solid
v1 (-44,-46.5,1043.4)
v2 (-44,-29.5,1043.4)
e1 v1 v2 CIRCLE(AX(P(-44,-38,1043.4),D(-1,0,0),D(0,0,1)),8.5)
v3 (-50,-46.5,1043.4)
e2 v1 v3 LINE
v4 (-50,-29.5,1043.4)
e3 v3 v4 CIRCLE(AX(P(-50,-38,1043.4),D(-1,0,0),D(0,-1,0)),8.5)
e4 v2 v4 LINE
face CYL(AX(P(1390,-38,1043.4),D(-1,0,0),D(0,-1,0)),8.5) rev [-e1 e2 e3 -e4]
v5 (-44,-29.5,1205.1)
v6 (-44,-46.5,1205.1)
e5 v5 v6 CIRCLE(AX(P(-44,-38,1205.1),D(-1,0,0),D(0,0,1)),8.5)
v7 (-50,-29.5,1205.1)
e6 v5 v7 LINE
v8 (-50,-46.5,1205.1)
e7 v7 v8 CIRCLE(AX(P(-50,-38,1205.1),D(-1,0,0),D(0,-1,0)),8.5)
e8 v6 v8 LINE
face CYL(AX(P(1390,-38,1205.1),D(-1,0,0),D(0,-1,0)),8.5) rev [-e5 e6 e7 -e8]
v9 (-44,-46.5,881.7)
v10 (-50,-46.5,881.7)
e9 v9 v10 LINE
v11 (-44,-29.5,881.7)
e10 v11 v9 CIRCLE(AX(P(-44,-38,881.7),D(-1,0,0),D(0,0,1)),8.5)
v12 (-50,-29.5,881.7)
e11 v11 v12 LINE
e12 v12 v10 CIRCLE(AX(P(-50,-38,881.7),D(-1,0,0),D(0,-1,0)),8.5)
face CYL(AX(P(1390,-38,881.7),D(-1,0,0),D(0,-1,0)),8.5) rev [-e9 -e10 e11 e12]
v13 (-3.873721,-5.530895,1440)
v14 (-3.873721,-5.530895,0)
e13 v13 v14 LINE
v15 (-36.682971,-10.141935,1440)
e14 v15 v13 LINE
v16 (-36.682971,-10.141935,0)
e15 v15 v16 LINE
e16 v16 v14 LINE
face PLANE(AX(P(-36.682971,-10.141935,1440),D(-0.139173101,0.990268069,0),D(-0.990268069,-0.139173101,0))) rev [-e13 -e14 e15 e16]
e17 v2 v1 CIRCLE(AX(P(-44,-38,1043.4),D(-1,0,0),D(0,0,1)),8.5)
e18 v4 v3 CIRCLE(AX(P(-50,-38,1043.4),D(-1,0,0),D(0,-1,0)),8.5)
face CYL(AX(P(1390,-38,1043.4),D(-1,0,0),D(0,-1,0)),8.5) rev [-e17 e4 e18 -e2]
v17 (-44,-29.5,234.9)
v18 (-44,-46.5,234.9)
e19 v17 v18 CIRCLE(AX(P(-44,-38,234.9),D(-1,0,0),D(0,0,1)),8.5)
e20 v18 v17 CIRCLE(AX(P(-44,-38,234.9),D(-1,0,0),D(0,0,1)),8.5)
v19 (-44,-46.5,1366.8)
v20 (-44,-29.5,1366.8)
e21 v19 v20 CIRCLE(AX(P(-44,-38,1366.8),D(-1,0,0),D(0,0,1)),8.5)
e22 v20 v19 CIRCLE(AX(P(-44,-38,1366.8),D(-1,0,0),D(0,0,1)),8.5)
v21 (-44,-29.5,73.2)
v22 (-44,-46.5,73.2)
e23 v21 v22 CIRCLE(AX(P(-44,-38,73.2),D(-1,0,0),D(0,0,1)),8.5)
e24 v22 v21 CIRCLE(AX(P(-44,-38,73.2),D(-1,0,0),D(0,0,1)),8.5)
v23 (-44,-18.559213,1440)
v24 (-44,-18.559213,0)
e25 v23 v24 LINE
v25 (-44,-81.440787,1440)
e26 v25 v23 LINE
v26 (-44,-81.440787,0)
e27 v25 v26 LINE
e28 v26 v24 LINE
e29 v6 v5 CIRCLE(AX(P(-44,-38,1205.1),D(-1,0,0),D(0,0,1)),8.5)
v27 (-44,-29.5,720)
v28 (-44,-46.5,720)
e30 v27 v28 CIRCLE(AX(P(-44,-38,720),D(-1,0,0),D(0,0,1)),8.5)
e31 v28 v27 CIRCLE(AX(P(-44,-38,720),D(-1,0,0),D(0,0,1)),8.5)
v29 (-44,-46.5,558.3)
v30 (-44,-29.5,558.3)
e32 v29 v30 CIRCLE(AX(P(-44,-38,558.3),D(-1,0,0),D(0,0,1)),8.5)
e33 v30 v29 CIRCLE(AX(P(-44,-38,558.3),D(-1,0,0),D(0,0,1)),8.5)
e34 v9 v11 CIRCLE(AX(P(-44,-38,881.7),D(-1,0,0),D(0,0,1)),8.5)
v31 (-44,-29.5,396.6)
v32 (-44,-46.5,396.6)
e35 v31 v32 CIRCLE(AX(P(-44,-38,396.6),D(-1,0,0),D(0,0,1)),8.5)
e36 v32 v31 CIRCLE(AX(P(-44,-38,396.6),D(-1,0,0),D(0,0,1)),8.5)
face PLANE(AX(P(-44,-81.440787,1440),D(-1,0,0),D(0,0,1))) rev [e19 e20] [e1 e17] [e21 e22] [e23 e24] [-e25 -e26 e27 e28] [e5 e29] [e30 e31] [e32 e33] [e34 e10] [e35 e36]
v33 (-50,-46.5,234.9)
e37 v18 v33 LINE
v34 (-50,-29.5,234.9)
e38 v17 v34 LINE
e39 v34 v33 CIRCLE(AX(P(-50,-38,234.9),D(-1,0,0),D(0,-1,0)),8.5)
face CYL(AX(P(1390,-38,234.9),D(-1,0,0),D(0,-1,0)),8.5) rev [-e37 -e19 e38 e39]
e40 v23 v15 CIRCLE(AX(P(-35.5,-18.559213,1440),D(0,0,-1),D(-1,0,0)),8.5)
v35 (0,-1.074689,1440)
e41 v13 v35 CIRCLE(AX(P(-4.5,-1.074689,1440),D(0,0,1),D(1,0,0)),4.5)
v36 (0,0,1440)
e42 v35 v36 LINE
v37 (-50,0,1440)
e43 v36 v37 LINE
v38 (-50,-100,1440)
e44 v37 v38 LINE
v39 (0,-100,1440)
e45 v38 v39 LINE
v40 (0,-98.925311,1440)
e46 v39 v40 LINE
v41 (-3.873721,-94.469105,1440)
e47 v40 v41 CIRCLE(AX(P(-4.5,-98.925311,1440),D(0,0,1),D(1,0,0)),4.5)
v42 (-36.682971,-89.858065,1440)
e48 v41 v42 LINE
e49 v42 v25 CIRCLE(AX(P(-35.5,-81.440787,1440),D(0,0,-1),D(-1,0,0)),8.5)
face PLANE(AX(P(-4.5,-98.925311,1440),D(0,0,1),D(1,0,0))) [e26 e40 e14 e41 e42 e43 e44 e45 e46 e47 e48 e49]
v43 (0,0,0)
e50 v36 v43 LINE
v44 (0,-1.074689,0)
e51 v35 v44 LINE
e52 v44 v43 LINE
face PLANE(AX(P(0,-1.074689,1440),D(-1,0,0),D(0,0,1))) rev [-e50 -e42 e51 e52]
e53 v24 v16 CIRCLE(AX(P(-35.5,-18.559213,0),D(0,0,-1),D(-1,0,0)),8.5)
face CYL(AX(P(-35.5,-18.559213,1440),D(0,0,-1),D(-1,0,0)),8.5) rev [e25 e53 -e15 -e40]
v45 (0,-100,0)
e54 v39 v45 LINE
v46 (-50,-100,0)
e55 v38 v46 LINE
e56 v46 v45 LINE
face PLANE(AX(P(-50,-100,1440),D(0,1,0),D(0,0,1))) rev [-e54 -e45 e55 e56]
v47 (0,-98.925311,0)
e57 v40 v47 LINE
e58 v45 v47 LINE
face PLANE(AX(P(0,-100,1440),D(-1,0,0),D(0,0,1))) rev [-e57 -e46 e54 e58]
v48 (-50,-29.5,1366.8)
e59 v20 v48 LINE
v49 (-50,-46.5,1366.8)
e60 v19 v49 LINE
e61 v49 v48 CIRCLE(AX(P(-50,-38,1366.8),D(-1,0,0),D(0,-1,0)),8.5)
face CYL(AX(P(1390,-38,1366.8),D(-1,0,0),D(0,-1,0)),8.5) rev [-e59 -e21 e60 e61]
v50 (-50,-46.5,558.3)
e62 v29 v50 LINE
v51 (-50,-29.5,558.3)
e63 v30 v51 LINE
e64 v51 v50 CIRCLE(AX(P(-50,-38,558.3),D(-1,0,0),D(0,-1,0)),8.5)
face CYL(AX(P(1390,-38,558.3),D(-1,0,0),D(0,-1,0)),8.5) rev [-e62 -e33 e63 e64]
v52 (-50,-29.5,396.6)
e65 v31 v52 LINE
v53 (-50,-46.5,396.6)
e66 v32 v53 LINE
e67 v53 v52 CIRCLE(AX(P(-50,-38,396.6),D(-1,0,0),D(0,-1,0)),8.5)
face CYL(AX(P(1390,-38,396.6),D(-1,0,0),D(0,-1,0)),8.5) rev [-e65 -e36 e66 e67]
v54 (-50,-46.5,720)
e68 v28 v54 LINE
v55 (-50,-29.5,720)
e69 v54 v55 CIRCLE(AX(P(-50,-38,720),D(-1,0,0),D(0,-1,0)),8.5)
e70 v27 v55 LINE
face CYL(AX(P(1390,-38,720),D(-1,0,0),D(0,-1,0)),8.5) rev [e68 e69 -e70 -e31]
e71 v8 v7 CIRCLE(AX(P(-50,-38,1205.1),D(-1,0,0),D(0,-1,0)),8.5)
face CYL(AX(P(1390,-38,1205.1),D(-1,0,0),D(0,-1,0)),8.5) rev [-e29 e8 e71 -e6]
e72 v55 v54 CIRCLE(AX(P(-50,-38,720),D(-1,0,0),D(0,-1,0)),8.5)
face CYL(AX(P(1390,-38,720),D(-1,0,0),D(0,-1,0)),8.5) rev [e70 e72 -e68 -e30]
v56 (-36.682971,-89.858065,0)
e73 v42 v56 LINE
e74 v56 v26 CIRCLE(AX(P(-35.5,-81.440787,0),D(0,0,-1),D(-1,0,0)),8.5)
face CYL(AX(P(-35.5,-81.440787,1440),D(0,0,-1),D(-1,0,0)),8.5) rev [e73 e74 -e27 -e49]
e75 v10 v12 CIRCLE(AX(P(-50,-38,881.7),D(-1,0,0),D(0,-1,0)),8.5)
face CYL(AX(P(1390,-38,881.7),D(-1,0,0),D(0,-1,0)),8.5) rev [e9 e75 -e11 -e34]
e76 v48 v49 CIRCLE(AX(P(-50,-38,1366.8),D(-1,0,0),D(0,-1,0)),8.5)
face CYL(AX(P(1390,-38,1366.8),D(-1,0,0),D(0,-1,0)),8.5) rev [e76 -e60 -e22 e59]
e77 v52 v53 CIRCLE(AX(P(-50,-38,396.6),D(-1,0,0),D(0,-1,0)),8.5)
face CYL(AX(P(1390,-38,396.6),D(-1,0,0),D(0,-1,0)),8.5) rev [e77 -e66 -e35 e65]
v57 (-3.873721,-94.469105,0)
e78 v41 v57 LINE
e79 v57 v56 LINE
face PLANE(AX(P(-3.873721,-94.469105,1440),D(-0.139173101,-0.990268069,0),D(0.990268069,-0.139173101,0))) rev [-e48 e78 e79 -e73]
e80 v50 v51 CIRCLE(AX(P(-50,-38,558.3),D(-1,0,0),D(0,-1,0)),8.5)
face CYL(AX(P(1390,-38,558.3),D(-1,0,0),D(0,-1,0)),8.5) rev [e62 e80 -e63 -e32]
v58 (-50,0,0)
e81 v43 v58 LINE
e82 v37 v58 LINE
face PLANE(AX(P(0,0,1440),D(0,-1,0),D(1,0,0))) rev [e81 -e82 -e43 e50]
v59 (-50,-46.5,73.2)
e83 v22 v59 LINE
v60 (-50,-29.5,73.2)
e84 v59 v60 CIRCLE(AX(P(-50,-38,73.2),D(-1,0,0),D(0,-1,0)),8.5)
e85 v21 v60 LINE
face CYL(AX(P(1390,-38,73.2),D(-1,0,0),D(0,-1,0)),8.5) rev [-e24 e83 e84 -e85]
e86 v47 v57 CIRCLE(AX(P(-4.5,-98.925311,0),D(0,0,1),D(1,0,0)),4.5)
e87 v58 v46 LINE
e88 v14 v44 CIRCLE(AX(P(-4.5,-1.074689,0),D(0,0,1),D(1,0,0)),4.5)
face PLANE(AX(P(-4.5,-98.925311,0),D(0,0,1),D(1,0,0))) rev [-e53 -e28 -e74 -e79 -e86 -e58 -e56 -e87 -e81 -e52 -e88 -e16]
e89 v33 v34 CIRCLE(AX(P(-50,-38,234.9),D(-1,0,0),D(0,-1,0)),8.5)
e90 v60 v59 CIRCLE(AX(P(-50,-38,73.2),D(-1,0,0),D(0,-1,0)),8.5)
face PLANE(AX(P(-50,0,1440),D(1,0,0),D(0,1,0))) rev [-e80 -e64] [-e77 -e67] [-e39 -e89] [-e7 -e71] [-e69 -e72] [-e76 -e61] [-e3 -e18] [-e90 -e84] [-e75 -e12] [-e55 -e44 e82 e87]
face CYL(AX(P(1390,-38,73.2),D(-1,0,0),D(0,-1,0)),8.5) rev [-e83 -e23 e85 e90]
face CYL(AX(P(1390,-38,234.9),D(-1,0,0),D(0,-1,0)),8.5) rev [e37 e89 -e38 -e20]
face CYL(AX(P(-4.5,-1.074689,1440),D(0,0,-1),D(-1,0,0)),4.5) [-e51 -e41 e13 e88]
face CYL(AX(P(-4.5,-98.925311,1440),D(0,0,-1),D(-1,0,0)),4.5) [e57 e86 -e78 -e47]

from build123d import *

# Parameters (mm, degrees)
BOSS_EXTRUDE1_DEPTH = 1440
SKETCH2_R           = 8.5
CUT_EXTRUDE1_DEPTH  = 1440


with BuildPart() as part:
    # Sketch1 → Boss-Extrude1 (new body)
    with BuildSketch(Plane.XY):
        with BuildLine():
            Line((0, 0), (-50, 0))
            Line((-50, 0), (-50, -100))
            Line((-50, -100), (0, -100))
            Line((0, -100), (0, -98.925311188))
            ThreePointArc((0, -98.925311188), (-1.103806889, -95.973045557), (-3.873721046, -94.469104878))
            Line((-3.873721046, -94.469104878), (-36.682971358, -89.858065454))
            ThreePointArc((-36.682971358, -89.858065454), (-41.915031432, -87.017288616), (-44, -81.440786869))
            Line((-44, -81.440786869), (-44, -18.559213131))
            ThreePointArc((-44, -18.559213131), (-41.915031432, -12.982711384), (-36.682971358, -10.141934546))
            Line((-36.682971358, -10.141934546), (-3.873721046, -5.530895122))
            ThreePointArc((-3.873721046, -5.530895122), (-1.103806889, -4.026954443), (0, -1.074688812))
            Line((0, -1.074688812), (0, 0))
        make_face()
    extrude(amount=BOSS_EXTRUDE1_DEPTH)

    # Sketch2 → Cut-Extrude1 (cut)
    with BuildSketch(Plane.ZY.offset(50)):
        with Locations(Location((73.2, -38, 0), (0, 0, 270))):
            Circle(SKETCH2_R)
        with Locations(Location((234.9, -38, 0), (0, 0, 270))):
            Circle(SKETCH2_R)
        with Locations(Location((396.6, -38, 0), (0, 0, 270))):
            Circle(SKETCH2_R)
        with Locations(Location((558.3, -38, 0), (0, 0, 270))):
            Circle(SKETCH2_R)
        with Locations(Location((720, -38, 0), (0, 0, 270))):
            Circle(SKETCH2_R)
        with Locations(Location((881.7, -38, 0), (0, 0, 270))):
            Circle(SKETCH2_R)
        with Locations(Location((1043.4, -38, 0), (0, 0, 270))):
            Circle(SKETCH2_R)
        with Locations(Location((1205.1, -38, 0), (0, 0, 270))):
            Circle(SKETCH2_R)
        with Locations(Location((1366.8, -38, 0), (0, 0, 270))):
            Circle(SKETCH2_R)
    extrude(amount=-CUT_EXTRUDE1_DEPTH, mode=Mode.SUBTRACT)


solid = part.part
